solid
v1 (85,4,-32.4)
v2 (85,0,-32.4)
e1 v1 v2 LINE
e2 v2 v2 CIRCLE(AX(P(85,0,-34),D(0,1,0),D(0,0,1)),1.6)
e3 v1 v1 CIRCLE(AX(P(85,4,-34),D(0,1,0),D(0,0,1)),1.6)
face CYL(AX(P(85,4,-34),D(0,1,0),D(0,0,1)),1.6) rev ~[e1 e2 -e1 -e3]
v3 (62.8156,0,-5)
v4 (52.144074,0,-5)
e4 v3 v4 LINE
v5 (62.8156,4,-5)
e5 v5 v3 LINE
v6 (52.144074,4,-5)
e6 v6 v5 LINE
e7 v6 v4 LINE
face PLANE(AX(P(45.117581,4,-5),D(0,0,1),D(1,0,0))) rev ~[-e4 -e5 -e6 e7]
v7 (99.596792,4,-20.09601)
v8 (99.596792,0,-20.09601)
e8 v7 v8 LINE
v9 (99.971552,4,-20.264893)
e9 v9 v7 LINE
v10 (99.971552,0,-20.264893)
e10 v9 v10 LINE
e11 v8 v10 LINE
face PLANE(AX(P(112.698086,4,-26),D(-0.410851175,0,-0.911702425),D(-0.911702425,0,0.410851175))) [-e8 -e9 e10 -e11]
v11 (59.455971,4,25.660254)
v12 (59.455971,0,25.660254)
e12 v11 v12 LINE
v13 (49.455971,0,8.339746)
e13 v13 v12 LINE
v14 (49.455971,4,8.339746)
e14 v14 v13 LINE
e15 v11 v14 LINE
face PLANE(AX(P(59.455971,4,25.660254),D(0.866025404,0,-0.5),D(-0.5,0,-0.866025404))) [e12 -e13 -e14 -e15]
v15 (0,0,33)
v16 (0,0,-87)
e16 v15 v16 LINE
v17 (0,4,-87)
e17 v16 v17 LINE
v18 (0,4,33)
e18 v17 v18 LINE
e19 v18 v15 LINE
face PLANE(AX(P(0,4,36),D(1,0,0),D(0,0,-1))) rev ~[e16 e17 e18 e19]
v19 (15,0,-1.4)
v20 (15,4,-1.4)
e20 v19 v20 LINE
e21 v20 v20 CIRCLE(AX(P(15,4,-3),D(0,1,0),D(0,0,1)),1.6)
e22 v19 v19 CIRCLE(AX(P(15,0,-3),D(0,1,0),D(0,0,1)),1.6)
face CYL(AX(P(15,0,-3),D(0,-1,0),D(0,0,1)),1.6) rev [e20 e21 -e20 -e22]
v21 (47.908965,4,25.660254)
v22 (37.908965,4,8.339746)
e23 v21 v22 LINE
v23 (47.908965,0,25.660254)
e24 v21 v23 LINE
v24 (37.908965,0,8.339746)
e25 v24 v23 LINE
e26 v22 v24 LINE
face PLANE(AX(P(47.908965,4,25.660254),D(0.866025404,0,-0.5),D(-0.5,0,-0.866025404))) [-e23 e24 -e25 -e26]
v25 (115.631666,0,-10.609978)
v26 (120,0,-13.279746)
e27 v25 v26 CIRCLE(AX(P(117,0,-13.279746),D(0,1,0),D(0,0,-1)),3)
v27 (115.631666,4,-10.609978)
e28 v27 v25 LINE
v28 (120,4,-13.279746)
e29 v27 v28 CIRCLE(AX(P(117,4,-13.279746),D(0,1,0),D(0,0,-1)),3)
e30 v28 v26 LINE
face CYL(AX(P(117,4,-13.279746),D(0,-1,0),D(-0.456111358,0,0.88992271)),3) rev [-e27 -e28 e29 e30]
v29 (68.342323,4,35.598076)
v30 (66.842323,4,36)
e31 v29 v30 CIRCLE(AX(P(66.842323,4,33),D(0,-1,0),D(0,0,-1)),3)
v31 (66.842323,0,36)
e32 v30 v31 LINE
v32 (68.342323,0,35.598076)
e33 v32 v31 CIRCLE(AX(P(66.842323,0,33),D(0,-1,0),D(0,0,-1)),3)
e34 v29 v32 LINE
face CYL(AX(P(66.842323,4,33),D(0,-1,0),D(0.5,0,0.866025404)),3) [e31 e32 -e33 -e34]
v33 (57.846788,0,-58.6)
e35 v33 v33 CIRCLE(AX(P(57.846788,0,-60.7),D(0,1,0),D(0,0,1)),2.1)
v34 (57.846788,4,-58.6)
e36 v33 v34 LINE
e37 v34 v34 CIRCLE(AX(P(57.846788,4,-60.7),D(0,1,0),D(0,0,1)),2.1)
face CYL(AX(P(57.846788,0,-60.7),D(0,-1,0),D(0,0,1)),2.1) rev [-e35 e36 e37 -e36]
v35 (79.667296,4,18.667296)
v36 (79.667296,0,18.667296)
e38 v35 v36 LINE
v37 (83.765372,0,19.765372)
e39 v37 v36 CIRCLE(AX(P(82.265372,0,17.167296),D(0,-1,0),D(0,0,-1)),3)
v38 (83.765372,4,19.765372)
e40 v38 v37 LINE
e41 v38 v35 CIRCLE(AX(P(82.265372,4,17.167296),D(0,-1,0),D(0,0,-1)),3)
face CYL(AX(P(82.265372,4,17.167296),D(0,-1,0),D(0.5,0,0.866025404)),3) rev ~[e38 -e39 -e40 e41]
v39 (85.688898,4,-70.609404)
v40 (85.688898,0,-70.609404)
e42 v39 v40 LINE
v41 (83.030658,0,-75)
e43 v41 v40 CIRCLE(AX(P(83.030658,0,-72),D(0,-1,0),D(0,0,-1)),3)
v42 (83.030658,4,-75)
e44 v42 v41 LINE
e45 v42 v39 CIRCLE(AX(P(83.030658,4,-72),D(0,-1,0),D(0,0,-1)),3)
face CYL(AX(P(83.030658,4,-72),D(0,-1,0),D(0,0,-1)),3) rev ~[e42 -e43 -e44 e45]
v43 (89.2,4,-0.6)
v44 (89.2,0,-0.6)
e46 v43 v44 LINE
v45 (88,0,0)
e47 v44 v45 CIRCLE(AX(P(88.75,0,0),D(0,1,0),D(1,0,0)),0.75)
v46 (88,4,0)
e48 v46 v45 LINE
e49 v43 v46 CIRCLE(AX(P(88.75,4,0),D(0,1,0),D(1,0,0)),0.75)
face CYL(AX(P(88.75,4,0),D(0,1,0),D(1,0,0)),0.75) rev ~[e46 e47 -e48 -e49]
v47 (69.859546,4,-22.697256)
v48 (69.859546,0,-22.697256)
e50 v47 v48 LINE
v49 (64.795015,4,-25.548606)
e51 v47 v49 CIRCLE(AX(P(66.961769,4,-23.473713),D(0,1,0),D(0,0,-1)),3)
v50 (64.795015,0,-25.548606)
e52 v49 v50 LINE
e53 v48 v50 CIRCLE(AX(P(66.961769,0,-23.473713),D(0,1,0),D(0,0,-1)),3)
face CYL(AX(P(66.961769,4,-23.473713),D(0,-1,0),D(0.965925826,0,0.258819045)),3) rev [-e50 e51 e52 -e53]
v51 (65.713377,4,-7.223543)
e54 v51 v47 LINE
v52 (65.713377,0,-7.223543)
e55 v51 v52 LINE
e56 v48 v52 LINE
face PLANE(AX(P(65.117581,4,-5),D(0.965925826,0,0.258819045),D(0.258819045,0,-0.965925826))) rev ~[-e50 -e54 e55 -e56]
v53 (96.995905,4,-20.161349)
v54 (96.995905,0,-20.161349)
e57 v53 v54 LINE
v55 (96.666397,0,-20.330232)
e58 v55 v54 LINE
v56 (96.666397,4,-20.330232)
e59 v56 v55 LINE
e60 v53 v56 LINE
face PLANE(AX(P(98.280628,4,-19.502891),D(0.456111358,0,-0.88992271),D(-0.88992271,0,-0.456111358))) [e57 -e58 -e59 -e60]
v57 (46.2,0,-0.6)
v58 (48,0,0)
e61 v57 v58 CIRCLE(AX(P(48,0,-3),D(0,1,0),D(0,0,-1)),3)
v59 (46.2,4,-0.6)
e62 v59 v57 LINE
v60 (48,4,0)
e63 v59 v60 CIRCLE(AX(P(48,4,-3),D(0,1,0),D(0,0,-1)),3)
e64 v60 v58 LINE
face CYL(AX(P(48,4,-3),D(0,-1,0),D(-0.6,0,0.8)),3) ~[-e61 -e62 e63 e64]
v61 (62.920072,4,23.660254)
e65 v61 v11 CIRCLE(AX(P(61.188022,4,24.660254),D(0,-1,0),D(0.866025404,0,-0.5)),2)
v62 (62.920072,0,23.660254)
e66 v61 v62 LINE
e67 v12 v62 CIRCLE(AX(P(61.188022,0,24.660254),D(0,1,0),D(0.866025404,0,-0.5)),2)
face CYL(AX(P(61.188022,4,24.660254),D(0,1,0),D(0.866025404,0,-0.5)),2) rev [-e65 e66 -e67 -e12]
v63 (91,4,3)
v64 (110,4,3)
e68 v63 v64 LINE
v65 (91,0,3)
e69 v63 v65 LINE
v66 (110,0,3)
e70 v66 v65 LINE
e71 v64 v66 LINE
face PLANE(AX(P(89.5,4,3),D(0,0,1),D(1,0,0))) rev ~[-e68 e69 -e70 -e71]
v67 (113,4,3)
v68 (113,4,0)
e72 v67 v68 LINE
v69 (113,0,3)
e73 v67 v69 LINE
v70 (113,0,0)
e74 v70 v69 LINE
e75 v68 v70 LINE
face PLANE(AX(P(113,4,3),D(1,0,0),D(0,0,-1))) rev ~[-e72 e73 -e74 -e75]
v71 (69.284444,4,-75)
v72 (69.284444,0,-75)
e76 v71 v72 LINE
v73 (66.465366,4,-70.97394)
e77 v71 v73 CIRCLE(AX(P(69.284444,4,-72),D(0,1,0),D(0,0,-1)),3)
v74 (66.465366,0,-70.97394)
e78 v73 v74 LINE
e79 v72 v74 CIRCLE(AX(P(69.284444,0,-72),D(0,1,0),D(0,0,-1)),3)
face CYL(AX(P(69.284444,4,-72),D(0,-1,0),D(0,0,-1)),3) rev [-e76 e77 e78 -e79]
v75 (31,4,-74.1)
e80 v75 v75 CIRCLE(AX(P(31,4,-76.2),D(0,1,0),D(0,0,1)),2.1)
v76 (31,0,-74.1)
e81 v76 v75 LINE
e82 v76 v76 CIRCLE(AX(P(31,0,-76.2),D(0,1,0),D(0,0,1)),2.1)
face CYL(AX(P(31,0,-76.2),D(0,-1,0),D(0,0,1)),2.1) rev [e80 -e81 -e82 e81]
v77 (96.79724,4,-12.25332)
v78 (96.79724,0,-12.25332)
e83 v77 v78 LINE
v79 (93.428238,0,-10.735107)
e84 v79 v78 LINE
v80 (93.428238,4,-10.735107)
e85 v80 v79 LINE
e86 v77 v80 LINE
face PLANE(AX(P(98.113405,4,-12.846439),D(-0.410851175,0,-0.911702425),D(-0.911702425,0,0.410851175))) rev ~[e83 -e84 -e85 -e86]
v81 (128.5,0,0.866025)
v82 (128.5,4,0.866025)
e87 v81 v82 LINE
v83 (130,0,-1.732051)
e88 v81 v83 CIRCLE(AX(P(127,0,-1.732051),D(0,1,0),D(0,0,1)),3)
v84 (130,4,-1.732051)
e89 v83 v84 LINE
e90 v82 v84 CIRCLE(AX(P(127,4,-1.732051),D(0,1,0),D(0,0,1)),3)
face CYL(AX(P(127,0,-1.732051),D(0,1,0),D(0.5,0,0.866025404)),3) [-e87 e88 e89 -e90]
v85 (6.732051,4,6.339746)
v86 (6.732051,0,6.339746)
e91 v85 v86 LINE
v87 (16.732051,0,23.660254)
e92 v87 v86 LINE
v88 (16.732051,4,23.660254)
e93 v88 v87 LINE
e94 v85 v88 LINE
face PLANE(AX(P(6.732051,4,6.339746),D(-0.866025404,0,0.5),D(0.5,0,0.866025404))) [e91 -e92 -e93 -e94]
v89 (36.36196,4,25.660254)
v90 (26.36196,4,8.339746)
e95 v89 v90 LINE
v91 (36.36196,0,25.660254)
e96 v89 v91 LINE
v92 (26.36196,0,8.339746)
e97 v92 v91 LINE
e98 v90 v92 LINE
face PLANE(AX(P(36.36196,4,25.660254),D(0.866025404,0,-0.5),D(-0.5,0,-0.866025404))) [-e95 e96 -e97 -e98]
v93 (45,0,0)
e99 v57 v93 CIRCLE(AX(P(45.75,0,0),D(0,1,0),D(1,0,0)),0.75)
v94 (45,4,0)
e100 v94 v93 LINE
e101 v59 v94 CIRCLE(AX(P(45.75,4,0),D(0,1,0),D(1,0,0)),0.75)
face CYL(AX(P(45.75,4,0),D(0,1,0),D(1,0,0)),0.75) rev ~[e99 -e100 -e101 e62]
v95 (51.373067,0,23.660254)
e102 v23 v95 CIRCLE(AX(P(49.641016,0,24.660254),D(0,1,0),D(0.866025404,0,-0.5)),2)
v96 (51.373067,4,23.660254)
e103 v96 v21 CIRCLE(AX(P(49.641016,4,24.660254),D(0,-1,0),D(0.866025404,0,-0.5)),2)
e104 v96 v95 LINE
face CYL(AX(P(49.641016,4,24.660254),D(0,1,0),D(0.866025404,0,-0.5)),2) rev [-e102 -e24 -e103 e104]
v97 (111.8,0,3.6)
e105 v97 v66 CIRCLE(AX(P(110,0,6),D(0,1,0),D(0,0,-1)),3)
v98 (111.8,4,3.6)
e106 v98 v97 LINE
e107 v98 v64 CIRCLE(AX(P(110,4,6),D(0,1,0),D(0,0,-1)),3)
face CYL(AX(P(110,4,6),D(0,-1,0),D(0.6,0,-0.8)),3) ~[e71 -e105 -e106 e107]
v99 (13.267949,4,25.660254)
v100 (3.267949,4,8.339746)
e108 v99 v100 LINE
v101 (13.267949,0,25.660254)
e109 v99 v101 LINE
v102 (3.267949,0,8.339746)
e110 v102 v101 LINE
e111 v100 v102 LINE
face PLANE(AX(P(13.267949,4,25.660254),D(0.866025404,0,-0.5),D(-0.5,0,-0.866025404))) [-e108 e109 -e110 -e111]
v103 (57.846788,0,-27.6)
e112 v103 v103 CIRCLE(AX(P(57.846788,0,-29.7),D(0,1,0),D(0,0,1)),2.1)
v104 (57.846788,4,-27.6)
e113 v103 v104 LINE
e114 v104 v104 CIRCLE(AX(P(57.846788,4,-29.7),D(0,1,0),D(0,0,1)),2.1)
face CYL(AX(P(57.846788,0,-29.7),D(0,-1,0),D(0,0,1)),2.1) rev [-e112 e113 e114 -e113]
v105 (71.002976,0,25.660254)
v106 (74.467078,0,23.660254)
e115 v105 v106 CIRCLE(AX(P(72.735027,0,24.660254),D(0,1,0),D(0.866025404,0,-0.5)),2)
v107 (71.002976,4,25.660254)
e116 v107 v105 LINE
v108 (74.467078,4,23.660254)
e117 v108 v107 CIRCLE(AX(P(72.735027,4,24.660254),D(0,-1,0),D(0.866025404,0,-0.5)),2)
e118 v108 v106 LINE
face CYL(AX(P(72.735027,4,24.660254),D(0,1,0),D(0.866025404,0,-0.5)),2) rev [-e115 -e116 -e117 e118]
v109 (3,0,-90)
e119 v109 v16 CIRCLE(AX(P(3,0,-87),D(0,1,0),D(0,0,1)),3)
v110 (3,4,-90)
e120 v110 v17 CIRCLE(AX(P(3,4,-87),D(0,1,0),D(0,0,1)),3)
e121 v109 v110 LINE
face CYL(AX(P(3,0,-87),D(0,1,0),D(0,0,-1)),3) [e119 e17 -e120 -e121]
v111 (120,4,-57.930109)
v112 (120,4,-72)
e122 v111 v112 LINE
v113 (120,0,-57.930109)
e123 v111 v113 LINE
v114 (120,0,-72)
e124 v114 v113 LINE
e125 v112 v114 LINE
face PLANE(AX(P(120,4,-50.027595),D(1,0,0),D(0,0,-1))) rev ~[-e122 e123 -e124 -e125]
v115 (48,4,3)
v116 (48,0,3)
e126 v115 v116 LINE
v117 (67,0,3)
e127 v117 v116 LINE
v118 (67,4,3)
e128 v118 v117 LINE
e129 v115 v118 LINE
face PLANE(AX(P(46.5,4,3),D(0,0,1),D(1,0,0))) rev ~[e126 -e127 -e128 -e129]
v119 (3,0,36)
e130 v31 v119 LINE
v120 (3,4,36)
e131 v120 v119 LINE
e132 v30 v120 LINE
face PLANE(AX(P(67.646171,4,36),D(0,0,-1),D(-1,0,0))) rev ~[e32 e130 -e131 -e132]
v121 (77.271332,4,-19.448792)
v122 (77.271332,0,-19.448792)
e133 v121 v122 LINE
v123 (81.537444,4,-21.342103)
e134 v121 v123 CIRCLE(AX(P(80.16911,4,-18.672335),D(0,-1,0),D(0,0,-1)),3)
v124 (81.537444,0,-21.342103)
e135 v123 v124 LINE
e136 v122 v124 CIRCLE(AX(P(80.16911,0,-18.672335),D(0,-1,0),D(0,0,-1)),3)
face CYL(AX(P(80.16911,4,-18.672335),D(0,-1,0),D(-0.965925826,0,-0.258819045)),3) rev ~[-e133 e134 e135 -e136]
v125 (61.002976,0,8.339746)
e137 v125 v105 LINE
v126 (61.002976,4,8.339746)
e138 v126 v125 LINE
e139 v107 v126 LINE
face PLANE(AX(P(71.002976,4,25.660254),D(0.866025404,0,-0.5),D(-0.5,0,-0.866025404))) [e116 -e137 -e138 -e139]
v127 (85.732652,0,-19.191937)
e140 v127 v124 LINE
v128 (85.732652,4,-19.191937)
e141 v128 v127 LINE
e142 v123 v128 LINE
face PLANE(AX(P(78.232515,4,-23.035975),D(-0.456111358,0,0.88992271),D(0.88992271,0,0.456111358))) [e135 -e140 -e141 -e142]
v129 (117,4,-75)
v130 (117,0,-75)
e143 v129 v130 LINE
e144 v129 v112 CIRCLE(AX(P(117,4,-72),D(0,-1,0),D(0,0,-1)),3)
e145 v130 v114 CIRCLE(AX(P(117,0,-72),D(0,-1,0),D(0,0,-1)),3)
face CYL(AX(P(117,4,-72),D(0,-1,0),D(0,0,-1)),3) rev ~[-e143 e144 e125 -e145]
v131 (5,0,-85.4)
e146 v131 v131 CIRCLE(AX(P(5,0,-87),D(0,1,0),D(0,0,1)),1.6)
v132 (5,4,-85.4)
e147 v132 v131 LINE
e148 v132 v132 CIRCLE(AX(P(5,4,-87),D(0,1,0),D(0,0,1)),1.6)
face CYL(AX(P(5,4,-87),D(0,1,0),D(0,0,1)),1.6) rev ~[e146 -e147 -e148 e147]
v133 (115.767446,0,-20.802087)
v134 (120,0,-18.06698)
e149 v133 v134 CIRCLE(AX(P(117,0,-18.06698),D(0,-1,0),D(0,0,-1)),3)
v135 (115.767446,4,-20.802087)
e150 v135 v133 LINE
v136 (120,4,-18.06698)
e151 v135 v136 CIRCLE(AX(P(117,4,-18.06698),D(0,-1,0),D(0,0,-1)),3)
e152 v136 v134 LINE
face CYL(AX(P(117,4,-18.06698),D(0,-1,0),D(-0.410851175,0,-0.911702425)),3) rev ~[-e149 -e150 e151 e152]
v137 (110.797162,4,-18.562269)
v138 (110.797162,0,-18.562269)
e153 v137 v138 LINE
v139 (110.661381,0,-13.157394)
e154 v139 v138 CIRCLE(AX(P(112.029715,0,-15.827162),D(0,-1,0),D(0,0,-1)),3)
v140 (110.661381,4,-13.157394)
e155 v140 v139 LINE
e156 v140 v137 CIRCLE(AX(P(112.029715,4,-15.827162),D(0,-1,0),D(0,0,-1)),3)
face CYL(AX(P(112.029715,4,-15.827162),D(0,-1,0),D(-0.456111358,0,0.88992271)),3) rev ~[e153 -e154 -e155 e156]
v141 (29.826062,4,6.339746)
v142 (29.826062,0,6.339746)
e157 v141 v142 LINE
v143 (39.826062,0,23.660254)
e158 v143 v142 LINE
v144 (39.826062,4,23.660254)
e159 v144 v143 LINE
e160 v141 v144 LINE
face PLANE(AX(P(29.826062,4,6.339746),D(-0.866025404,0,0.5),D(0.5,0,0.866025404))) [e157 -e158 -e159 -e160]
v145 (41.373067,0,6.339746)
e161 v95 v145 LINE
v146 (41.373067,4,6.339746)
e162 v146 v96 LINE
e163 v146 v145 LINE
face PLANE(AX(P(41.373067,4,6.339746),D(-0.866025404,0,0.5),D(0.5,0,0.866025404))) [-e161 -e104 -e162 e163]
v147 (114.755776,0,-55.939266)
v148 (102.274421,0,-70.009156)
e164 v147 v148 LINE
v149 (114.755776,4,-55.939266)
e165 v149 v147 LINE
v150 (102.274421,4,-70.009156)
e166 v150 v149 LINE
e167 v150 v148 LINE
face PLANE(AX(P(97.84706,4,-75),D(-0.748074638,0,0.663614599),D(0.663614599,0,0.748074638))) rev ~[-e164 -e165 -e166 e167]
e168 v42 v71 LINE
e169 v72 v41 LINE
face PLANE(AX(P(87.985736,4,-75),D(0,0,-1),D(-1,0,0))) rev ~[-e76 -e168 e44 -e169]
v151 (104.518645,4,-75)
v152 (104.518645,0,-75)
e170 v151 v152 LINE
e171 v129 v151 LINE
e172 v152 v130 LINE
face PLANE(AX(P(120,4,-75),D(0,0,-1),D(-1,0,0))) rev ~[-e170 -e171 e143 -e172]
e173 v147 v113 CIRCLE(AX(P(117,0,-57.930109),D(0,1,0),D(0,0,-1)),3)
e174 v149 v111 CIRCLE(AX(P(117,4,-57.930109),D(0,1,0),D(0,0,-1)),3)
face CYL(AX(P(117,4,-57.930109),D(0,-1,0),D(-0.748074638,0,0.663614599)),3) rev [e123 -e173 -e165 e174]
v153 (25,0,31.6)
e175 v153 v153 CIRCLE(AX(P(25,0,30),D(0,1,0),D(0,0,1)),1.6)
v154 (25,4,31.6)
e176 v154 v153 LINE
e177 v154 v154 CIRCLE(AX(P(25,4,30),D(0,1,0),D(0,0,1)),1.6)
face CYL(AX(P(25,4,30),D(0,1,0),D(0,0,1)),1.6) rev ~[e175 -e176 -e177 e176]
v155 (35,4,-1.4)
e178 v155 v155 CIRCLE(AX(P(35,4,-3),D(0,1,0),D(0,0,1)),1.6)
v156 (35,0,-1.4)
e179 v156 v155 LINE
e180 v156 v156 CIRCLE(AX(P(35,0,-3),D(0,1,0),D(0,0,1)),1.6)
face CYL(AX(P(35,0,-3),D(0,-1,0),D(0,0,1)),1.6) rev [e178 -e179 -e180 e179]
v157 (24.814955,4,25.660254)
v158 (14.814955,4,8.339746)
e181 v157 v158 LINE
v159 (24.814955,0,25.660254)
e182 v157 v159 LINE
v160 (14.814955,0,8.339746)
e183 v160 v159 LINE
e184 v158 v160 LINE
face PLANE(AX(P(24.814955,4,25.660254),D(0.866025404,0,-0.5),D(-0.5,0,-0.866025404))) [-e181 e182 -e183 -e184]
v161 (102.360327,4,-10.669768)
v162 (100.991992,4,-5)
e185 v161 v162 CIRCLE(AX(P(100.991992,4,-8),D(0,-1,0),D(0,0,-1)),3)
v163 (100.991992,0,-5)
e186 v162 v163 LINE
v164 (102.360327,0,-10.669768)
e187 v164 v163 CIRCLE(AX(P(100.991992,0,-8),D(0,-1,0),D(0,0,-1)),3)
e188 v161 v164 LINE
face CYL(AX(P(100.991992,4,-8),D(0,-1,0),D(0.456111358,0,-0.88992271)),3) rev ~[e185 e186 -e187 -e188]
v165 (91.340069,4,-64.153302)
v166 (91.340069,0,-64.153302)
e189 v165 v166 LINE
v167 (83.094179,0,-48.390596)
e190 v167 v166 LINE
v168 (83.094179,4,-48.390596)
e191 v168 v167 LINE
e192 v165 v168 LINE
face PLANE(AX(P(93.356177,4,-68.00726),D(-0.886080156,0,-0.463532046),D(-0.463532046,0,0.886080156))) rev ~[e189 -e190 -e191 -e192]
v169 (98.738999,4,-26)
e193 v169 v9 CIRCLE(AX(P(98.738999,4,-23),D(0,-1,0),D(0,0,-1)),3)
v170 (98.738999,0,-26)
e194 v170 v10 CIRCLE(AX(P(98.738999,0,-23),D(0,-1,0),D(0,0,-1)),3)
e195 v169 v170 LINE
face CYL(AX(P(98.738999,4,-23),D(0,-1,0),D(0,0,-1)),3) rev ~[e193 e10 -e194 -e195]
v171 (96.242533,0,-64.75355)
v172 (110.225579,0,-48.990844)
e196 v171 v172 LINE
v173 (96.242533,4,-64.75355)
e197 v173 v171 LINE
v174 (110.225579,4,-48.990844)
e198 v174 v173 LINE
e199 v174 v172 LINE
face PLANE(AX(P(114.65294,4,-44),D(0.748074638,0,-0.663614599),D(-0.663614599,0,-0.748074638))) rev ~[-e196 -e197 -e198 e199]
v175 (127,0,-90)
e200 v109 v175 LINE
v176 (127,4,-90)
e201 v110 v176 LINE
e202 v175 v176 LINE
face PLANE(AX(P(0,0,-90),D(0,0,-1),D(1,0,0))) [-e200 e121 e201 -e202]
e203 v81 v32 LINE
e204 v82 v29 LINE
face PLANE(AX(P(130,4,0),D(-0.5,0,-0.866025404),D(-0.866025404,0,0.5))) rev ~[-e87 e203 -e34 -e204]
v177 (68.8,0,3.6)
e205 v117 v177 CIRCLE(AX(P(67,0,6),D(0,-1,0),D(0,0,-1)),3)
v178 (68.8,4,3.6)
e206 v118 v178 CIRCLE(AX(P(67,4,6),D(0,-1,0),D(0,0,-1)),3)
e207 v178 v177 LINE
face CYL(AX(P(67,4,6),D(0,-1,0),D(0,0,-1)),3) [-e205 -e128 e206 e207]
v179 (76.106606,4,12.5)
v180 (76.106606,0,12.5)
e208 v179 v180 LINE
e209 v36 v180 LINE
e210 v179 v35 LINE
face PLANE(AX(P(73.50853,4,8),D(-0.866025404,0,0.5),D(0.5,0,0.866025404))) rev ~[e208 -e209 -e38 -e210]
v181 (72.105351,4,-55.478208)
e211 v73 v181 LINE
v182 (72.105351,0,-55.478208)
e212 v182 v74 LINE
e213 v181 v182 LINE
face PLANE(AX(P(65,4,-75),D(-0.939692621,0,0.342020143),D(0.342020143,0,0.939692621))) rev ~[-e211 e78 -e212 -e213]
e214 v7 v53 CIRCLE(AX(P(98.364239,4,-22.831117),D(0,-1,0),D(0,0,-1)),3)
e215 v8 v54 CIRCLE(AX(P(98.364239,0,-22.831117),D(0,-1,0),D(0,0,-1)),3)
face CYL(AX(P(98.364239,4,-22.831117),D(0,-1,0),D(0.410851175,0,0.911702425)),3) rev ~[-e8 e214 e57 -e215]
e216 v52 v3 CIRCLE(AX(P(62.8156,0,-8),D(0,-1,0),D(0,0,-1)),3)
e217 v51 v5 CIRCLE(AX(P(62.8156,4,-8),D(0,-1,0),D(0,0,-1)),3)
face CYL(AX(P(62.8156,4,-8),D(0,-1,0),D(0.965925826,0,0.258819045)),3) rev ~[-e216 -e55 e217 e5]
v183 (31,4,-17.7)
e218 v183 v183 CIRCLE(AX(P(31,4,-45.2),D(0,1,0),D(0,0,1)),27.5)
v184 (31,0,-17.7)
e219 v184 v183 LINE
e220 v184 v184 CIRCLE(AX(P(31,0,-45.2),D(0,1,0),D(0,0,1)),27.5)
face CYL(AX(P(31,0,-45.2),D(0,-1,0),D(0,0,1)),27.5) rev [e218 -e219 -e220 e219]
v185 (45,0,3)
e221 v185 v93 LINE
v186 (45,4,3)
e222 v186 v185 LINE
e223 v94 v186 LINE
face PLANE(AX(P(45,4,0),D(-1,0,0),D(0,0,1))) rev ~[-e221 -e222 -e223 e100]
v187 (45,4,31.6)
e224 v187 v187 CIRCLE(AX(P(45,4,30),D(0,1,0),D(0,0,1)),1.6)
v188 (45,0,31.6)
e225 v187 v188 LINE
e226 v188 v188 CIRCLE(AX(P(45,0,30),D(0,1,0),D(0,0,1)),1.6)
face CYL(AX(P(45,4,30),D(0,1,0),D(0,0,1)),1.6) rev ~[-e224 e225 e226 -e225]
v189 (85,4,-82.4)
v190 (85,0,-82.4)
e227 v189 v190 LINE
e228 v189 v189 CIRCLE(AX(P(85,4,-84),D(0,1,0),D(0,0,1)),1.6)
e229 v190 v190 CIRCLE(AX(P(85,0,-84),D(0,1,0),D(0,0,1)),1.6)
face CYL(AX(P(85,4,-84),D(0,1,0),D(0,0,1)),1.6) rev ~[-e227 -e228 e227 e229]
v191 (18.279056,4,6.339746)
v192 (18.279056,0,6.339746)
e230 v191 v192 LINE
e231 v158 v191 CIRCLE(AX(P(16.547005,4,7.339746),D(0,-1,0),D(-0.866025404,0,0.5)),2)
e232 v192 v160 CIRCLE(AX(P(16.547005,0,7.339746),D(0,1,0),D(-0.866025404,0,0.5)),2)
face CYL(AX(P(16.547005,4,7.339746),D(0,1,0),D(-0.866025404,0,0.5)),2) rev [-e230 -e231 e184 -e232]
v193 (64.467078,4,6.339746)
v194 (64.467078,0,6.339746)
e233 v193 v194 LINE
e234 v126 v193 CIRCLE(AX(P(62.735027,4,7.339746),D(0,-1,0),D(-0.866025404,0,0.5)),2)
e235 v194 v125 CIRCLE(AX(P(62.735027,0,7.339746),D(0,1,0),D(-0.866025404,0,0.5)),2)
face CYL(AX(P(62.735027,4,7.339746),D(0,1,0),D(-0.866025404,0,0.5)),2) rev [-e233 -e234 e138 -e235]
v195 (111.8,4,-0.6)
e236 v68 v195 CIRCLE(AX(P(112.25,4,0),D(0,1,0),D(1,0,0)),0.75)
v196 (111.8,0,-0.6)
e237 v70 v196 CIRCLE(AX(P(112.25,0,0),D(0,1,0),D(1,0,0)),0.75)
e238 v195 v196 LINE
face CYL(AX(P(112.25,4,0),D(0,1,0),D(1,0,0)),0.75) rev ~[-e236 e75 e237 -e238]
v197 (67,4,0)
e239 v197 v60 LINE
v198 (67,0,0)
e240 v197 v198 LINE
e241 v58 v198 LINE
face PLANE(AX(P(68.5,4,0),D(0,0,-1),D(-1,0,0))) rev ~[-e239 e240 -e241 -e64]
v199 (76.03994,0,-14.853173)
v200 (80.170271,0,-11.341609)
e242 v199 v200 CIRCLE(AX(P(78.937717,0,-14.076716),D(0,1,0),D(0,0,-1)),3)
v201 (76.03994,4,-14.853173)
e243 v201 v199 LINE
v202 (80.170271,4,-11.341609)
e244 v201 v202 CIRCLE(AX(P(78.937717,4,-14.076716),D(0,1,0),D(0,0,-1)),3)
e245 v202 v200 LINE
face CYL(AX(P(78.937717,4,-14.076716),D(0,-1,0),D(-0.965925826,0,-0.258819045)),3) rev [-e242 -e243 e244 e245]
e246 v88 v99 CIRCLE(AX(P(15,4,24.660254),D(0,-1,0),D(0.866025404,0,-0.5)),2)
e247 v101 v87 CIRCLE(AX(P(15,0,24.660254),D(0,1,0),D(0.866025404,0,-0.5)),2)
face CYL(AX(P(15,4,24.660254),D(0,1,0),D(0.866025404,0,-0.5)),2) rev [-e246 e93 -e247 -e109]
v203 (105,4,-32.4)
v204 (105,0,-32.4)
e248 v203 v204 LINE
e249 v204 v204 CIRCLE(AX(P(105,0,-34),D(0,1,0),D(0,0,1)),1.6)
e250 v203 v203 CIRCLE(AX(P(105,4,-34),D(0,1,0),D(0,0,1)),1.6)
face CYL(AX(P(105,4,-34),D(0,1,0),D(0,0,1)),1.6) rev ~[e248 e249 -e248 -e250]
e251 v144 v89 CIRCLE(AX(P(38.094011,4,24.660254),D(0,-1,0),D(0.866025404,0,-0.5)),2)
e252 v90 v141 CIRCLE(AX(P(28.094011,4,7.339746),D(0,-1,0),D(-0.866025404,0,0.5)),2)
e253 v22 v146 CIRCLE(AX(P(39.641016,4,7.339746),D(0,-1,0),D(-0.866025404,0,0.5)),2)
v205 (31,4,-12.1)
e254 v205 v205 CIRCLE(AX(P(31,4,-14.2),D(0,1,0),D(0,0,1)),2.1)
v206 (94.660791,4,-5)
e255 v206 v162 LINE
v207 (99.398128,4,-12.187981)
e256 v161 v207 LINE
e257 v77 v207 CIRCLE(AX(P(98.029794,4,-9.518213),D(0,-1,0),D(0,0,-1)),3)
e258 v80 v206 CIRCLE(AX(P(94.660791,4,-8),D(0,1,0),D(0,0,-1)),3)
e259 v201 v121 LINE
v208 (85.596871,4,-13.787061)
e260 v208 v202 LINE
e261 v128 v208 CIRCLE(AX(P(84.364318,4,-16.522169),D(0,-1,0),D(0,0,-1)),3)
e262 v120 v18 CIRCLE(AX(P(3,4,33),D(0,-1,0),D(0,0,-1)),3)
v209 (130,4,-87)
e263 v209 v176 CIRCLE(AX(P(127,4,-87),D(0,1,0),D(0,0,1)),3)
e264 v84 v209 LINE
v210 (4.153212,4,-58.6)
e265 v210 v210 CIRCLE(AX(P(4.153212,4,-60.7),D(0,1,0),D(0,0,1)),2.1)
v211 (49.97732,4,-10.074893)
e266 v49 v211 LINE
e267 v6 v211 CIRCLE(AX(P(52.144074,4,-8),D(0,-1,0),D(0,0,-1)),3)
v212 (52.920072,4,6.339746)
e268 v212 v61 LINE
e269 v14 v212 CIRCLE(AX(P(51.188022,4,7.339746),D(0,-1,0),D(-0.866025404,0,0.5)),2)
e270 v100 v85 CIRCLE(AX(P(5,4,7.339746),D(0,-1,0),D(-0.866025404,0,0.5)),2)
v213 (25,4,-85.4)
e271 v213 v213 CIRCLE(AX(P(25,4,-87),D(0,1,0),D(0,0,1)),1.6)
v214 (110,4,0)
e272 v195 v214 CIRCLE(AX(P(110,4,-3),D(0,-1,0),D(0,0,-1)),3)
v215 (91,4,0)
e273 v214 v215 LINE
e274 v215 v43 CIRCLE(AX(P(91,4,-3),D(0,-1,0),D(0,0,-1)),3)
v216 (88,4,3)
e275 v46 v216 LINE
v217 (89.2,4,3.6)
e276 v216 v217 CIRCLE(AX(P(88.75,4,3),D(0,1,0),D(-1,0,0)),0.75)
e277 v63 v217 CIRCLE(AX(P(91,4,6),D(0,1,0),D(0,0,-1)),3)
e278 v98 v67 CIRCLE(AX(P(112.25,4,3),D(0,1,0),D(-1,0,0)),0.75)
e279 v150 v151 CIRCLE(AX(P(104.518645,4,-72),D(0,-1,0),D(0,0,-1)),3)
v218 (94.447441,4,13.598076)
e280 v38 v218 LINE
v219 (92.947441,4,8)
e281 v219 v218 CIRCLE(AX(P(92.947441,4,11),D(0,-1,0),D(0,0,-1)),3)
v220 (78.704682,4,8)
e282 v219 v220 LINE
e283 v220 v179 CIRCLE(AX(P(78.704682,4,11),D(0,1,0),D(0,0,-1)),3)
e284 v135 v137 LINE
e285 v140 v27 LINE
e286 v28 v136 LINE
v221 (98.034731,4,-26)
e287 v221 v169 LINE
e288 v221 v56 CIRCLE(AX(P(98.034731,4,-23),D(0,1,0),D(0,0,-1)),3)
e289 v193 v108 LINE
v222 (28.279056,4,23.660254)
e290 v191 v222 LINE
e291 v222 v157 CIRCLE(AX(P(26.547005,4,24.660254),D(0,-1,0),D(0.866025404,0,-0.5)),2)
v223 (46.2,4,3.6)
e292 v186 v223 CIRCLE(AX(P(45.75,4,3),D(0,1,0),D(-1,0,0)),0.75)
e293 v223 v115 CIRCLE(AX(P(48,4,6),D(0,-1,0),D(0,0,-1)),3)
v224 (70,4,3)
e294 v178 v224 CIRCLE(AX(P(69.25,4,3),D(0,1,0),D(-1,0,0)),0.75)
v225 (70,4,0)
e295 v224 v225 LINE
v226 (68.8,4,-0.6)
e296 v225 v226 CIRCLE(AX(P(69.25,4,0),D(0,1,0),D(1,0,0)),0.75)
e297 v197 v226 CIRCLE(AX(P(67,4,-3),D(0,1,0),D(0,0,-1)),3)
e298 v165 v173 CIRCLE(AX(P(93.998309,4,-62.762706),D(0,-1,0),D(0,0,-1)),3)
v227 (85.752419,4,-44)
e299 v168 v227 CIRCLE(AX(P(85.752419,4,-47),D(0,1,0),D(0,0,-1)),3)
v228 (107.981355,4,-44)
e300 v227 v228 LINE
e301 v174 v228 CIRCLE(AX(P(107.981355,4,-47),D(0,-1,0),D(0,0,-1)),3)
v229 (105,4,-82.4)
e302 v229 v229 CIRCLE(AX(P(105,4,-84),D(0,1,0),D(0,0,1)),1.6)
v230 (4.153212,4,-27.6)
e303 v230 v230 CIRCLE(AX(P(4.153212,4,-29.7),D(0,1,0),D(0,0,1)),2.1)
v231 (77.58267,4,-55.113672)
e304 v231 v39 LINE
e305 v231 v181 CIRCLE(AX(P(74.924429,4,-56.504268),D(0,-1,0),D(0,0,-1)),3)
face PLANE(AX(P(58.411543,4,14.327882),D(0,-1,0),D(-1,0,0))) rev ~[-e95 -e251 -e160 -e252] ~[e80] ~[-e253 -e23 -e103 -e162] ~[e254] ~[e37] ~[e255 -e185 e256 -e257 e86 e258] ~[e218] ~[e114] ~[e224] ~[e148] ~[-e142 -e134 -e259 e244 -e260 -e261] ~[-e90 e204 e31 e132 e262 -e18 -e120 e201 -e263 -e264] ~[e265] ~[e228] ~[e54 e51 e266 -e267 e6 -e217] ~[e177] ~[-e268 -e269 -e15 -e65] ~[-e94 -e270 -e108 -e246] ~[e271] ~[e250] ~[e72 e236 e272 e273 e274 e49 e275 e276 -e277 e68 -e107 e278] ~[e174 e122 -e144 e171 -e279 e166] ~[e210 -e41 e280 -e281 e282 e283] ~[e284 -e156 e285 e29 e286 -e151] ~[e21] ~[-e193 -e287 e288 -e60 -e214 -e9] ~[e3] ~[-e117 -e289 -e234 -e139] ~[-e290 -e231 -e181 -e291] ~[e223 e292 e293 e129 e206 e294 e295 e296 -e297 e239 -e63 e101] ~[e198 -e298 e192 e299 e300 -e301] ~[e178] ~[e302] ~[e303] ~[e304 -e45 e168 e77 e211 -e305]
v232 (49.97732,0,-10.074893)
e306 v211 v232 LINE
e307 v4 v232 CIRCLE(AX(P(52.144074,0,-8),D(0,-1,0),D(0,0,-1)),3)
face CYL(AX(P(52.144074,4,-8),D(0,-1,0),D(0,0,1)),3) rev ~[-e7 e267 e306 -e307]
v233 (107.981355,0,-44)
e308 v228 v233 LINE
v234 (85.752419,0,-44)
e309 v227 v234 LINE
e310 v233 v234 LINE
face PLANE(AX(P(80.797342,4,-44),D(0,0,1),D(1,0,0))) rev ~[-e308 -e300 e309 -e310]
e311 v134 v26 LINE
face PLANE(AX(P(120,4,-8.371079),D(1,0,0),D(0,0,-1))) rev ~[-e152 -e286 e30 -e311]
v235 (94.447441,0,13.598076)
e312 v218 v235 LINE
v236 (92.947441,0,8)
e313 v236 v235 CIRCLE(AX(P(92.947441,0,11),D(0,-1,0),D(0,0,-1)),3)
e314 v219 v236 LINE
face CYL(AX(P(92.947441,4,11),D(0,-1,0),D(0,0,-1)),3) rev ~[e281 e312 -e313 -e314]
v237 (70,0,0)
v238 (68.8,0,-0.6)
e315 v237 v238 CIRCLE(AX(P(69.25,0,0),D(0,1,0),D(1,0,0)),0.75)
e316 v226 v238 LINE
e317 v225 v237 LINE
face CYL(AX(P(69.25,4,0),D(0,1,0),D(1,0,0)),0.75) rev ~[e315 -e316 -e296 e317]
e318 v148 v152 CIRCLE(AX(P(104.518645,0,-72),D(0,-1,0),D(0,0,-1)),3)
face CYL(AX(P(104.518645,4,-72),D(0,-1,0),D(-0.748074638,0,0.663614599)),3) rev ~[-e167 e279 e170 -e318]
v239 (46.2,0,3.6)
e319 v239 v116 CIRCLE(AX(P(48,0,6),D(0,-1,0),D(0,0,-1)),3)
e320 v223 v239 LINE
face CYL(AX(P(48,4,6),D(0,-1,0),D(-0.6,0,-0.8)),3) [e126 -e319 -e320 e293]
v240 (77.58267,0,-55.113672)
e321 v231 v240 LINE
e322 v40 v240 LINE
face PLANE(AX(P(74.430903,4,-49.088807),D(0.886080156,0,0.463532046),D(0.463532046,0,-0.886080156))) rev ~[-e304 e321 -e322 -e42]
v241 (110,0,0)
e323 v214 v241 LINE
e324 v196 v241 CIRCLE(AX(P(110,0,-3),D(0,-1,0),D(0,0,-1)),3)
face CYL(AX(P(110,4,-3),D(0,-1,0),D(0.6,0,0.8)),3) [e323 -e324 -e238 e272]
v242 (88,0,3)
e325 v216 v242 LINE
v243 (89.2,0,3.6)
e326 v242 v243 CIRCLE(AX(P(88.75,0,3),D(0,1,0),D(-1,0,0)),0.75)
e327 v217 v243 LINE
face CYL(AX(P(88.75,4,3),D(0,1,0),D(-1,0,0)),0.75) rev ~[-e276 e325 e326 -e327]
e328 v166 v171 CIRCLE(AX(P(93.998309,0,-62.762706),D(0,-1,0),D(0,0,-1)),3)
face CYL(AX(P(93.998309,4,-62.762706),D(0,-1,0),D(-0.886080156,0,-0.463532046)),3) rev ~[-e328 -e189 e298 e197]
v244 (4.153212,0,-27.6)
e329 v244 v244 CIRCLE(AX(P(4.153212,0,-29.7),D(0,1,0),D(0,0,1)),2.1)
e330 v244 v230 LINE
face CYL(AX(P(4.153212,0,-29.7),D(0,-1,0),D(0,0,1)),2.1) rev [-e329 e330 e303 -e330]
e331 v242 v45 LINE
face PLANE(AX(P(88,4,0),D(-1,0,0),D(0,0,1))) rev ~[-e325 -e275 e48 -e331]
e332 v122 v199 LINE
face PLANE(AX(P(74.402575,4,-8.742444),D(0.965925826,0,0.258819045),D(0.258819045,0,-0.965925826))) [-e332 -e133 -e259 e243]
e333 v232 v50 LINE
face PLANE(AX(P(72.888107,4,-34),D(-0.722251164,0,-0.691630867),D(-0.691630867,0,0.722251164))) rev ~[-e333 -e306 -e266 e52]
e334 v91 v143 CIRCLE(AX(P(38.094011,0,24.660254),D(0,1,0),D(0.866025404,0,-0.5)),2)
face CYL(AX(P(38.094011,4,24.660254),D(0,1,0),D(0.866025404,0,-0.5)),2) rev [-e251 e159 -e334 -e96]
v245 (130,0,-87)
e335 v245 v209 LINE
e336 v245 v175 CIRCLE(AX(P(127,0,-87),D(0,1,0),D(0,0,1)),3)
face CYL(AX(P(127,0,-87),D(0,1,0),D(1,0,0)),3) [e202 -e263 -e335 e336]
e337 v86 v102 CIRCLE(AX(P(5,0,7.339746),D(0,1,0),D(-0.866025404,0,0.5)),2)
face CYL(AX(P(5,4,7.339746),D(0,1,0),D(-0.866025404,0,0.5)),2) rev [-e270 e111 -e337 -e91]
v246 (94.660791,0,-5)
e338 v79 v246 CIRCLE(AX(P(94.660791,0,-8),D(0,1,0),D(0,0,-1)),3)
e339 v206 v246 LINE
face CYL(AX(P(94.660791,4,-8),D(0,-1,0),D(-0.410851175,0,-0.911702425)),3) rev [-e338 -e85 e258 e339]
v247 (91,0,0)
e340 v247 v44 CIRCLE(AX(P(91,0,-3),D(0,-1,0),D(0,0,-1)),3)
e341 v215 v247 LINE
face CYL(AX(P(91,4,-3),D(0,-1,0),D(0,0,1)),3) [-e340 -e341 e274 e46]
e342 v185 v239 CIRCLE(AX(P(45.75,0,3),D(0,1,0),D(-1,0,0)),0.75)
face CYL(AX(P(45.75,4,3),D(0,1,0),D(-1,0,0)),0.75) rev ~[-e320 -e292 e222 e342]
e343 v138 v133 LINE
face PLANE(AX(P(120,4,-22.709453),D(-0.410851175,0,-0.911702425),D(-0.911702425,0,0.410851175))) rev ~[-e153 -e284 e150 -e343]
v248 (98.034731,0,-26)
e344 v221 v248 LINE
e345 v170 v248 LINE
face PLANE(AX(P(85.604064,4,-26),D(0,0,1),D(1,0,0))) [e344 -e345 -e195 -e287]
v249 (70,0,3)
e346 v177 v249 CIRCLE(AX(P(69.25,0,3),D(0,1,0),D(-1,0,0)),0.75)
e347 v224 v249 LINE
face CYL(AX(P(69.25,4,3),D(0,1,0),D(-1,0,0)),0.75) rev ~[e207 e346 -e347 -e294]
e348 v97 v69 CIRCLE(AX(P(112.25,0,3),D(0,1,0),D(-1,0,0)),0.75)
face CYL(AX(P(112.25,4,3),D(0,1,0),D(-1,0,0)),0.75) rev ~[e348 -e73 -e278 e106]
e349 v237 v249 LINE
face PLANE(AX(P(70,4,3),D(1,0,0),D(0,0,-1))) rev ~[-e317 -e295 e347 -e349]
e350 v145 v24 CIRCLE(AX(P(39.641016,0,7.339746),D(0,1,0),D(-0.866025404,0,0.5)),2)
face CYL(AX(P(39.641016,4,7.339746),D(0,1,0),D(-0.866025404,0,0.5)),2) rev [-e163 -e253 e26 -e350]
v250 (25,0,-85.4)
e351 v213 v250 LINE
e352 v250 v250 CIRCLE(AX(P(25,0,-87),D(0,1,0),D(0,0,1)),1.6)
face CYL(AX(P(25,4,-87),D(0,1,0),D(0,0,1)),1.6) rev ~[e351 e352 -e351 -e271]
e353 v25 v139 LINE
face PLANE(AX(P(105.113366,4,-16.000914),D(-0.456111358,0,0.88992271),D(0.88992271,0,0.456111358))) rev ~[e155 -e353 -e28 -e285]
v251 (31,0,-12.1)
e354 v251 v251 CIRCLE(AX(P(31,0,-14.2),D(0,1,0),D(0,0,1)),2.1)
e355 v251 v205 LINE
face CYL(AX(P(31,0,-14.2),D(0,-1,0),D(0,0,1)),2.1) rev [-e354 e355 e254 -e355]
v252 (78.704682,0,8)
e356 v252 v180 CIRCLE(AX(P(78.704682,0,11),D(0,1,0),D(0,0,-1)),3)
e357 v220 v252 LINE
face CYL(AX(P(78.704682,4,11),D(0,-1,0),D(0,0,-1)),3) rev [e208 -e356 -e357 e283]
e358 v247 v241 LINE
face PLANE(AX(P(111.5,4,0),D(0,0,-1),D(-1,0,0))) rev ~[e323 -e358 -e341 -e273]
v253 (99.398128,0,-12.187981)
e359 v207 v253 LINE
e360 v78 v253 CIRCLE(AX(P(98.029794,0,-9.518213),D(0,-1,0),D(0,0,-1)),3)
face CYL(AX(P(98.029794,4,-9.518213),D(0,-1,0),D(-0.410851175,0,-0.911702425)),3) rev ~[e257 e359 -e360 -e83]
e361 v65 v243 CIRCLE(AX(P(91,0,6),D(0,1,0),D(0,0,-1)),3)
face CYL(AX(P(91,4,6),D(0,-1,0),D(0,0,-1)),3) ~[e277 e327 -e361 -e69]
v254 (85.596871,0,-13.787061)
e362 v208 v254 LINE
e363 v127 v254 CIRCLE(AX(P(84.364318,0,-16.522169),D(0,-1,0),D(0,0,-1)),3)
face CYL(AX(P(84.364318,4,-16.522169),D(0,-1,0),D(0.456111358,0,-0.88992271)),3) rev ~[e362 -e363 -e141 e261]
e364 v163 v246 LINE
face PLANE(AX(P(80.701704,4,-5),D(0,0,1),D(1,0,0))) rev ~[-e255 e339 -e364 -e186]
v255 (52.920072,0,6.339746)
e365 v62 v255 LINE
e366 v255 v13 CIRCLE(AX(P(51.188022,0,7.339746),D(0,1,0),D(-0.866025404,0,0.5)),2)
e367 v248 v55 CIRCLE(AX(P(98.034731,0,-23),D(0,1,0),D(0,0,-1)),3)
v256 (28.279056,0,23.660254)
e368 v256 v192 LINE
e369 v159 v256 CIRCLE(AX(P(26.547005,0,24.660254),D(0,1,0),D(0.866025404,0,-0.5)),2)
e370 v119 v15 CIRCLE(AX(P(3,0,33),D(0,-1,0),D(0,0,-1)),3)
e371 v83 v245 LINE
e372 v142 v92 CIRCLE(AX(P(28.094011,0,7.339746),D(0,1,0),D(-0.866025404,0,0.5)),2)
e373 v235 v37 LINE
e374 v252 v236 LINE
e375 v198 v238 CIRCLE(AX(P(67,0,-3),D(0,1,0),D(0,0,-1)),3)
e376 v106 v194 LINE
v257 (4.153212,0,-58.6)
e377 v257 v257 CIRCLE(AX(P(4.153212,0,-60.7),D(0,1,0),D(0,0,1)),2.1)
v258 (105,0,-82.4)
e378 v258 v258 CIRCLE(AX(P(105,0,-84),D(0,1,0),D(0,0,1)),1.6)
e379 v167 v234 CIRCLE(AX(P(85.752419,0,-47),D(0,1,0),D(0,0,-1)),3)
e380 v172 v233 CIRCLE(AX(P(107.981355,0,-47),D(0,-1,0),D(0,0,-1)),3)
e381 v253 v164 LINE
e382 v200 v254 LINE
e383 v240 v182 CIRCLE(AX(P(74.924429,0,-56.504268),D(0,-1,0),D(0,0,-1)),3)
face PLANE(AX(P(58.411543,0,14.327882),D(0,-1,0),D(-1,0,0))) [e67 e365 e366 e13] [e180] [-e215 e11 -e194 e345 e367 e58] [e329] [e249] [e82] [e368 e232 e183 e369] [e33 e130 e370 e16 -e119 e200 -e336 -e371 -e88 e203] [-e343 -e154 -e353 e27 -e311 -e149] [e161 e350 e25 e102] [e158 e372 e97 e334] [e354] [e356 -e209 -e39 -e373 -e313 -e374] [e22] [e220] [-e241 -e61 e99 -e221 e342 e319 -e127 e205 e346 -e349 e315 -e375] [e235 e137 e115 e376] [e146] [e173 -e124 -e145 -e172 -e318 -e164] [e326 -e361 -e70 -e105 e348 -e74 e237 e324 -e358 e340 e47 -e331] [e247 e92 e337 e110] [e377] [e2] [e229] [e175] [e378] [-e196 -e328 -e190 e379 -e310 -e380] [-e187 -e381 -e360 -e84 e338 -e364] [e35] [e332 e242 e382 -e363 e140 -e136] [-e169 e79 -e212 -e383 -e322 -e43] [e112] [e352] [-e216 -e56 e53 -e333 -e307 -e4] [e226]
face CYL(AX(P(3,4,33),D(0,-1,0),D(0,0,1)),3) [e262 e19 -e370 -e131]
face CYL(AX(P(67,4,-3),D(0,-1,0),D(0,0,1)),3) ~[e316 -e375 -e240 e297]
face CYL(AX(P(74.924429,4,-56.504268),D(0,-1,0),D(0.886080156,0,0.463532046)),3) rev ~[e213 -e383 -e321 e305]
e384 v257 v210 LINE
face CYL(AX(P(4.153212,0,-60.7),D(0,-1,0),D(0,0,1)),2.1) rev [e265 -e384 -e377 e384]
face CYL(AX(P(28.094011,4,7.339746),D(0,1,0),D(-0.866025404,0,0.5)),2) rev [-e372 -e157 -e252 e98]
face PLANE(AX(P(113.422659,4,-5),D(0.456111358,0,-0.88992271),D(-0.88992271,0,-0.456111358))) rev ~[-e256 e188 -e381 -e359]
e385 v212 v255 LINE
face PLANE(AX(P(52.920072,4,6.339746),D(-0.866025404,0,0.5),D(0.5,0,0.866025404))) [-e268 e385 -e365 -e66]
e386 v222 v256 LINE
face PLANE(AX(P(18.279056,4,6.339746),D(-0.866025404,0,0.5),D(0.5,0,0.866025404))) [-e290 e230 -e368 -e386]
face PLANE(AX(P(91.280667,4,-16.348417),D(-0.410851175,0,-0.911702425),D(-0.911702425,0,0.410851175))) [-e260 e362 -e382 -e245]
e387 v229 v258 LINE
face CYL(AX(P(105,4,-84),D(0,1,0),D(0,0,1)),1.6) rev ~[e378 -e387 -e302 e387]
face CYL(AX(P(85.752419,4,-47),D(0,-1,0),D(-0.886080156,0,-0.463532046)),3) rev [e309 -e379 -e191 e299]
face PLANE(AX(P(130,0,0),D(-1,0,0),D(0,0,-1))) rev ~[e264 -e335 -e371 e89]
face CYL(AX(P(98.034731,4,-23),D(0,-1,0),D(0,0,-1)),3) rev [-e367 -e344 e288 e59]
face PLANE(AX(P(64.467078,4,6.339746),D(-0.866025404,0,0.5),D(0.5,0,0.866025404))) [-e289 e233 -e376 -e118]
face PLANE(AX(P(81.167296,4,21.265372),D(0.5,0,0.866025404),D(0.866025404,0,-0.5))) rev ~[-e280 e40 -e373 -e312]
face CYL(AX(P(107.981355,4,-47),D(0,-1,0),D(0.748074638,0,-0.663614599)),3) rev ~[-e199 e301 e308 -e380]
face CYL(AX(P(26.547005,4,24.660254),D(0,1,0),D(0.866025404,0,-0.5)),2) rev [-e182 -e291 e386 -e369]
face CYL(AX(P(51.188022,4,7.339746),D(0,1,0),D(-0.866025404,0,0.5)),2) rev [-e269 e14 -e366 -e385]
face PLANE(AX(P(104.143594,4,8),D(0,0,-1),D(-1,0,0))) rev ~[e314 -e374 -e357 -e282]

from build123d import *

# Parameters (mm, degrees)
SKETCH_1_W          = 130
SKETCH_1_H          = 90
SKETCH_1_R          = 27.5
SKETCH_1_R_2        = 2.1
SKETCH_1_R_3        = 1.6
EXTRUDE_1_DEPTH     = 4
EXTRUDE_2_DEPTH     = 4
SKETCH_3_R          = 1.6
CUT_EXTRUDE_1_DEPTH = 10
SKETCH_4_R          = 1.6
CUT_EXTRUDE_2_DEPTH = 10
CUT_EXTRUDE_3_DEPTH = 10
FILLET_1_R          = 3
CUT_EXTRUDE_4_DEPTH = 10
FILLET_2_R          = 3


with BuildPart() as part:
    # 草图1 → 凸台-拉伸1 (new body)
    with BuildSketch(Plane(origin=(0, 0, 0), x_dir=(1, 0, 0), z_dir=(0, 1, 0))):
        with Locations((65, 45)):
            Rectangle(SKETCH_1_W, SKETCH_1_H)
        with Locations(Location((31, 45.2, 0), (0, 0, 270))):
            Circle(SKETCH_1_R, mode=Mode.SUBTRACT)
        with Locations(Location((31, 76.2, 0), (0, 0, 270))):
            Circle(SKETCH_1_R_2, mode=Mode.SUBTRACT)
        with Locations(Location((57.846787517, 60.7, 0), (0, 0, 270))):
            Circle(SKETCH_1_R_2, mode=Mode.SUBTRACT)
        with Locations(Location((57.846787517, 29.7, 0), (0, 0, 270))):
            Circle(SKETCH_1_R_2, mode=Mode.SUBTRACT)
        with Locations(Location((31, 14.2, 0), (0, 0, 270))):
            Circle(SKETCH_1_R_2, mode=Mode.SUBTRACT)
        with Locations(Location((4.153212483, 29.7, 0), (0, 0, 270))):
            Circle(SKETCH_1_R_2, mode=Mode.SUBTRACT)
        with Locations(Location((4.153212483, 60.7, 0), (0, 0, 270))):
            Circle(SKETCH_1_R_2, mode=Mode.SUBTRACT)
        with Locations(Location((15, 3, 0), (0, 0, 270))):
            Circle(SKETCH_1_R_3, mode=Mode.SUBTRACT)
        with Locations(Location((35, 3, 0), (0, 0, 270))):
            Circle(SKETCH_1_R_3, mode=Mode.SUBTRACT)
    extrude(amount=EXTRUDE_1_DEPTH)

    # 草图2 → 凸台-拉伸2 (add)
    with BuildSketch(Plane(origin=(0, 4, 0), x_dir=(1, 0, 0), z_dir=(0, 1, 0))):
        Polygon((130, 0), (67.646170928, -36), (0, -36), (0, 0), align=None)
    extrude(amount=-EXTRUDE_2_DEPTH)

    # 草图3 → 切除-拉伸1 (cut)
    with BuildSketch(Plane(origin=(0, 4, 0), x_dir=(1, 0, 0), z_dir=(0, 1, 0))):
        with Locations(Location((25, -30, 0), (0, 0, 270))):
            Circle(SKETCH_3_R)
        with Locations(Location((45, -30, 0), (0, 0, 270))):
            Circle(SKETCH_3_R)
    extrude(amount=-CUT_EXTRUDE_1_DEPTH, mode=Mode.SUBTRACT)

    # 草图4 → 切除-拉伸2 (cut)
    with BuildSketch(Plane(origin=(0, 4, 0), x_dir=(1, 0, 0), z_dir=(0, 1, 0))):
        with Locations(Location((85, 84, 0), (0, 0, 270))):
            Circle(SKETCH_4_R)
        with Locations(Location((105, 84, 0), (0, 0, 270))):
            Circle(SKETCH_4_R)
        with Locations(Location((85, 34, 0), (0, 0, 270))):
            Circle(SKETCH_4_R)
        with Locations(Location((105, 34, 0), (0, 0, 270))):
            Circle(SKETCH_4_R)
        with Locations(Location((5, 87, 0), (0, 0, 270))):
            Circle(SKETCH_4_R)
        with Locations(Location((25, 87, 0), (0, 0, 270))):
            Circle(SKETCH_4_R)
    extrude(amount=-CUT_EXTRUDE_2_DEPTH, mode=Mode.SUBTRACT)

    # 草图2<3> → 切除-拉伸3 (cut)
    with BuildSketch(Plane(origin=(0, 4, 0), x_dir=(1, 0, 0), z_dir=(0, 1, 0))):
        with BuildLine():
            Line((46.5, 0), (45, 0))
            Line((45, 0), (45, -3))
            ThreePointArc((45, -3), (45.75, -3.75), (46.5, -3))
            Line((46.5, -3), (68.5, -3))
            ThreePointArc((68.5, -3), (69.25, -3.75), (70, -3))
            Line((70, -3), (70, 0))
            Line((70, 0), (68.5, 0))
            Line((68.5, 0), (46.5, 0))
        make_face()
        with BuildLine():
            Line((113, -3), (113, 0))
            Line((113, 0), (111.5, 0))
            Line((111.5, 0), (89.5, 0))
            Line((89.5, 0), (88, 0))
            Line((88, 0), (88, -3))
            ThreePointArc((88, -3), (88.75, -3.75), (89.5, -3))
            Line((89.5, -3), (111.5, -3))
            ThreePointArc((111.5, -3), (112.25, -3.75), (113, -3))
        make_face()
        with BuildLine():
            ThreePointArc((46.5, 0), (45.75, 0.75), (45, 0))
            Line((45, 0), (46.5, 0))
        make_face()
        with BuildLine():
            Line((68.5, 0), (70, 0))
            ThreePointArc((70, 0), (69.25, 0.75), (68.5, 0))
        make_face()
        with BuildLine():
            Line((88, 0), (89.5, 0))
            ThreePointArc((89.5, 0), (88.75, 0.75), (88, 0))
        make_face()
        with BuildLine():
            Line((111.5, 0), (113, 0))
            ThreePointArc((113, 0), (112.25, 0.75), (111.5, 0))
        make_face()
    extrude(amount=-CUT_EXTRUDE_3_DEPTH, mode=Mode.SUBTRACT)

    # 圆角1
    fillet_1_edges = [part.edges().sort_by_distance(p)[0] for p in [
        (67.646170928, 2, 36),
        (0, 2, 36),
        (0, 2, -90),
        (130, 2, -90),
        (130, 2, 0),
    ]]
    fillet(fillet_1_edges, radius=FILLET_1_R)

    # 草图5 → 切除-拉伸4 (cut)
    with BuildSketch(Plane(origin=(0, 4, 0), x_dir=(1, 0, 0), z_dir=(0, 1, 0))):
        with BuildLine():
            Line((6.732050808, -6.339745962), (16.732050808, -23.660254038))
            ThreePointArc((16.732050808, -23.660254038), (16, -26.392304845), (13.267949192, -25.660254038))
            Line((13.267949192, -25.660254038), (3.267949192, -8.339745962))
            ThreePointArc((3.267949192, -8.339745962), (4, -5.607695155), (6.732050808, -6.339745962))
        make_face()
        with BuildLine():
            Line((18.279056191, -6.339745962), (28.279056191, -23.660254038))
            ThreePointArc((28.279056191, -23.660254038), (27.547005384, -26.392304845), (24.814954576, -25.660254038))
            Line((24.814954576, -25.660254038), (14.814954576, -8.339745962))
            ThreePointArc((14.814954576, -8.339745962), (15.547005384, -5.607695155), (18.279056191, -6.339745962))
        make_face()
        with BuildLine():
            Line((29.826061575, -6.339745962), (39.826061575, -23.660254038))
            ThreePointArc((39.826061575, -23.660254038), (39.094010768, -26.392304845), (36.36195996, -25.660254038))
            Line((36.36195996, -25.660254038), (26.36195996, -8.339745962))
            ThreePointArc((26.36195996, -8.339745962), (27.094010768, -5.607695155), (29.826061575, -6.339745962))
        make_face()
        with BuildLine():
            Line((41.373066959, -6.339745962), (51.373066959, -23.660254038))
            ThreePointArc((51.373066959, -23.660254038), (50.641016151, -26.392304845), (47.908965344, -25.660254038))
            Line((47.908965344, -25.660254038), (37.908965344, -8.339745962))
            ThreePointArc((37.908965344, -8.339745962), (38.641016151, -5.607695155), (41.373066959, -6.339745962))
        make_face()
        with BuildLine():
            Line((52.920072343, -6.339745962), (62.920072343, -23.660254038))
            ThreePointArc((62.920072343, -23.660254038), (62.188021535, -26.392304845), (59.455970728, -25.660254038))
            Line((59.455970728, -25.660254038), (49.455970728, -8.339745962))
            ThreePointArc((49.455970728, -8.339745962), (50.188021535, -5.607695155), (52.920072343, -6.339745962))
        make_face()
        with BuildLine():
            Line((64.467077727, -6.339745962), (74.467077727, -23.660254038))
            ThreePointArc((74.467077727, -23.660254038), (73.735026919, -26.392304845), (71.002976111, -25.660254038))
            Line((71.002976111, -25.660254038), (61.002976111, -8.339745962))
            ThreePointArc((61.002976111, -8.339745962), (61.735026919, -5.607695155), (64.467077727, -6.339745962))
        make_face()
        Polygon((73.508529611, -8), (81.167295593, -21.265371804), (104.143593539, -8), align=None)
        Polygon((65, 75), (74.430902982, 49.088807011), (87.985735716, 75), align=None)
        Polygon((80.797341547, 44), (114.652939968, 44), (93.356176649, 68.007260469), align=None)
        Polygon((120, 50.027594945), (120, 75), (97.847060032, 75), align=None)
        Polygon((72.888107353, 34), (45.117580773, 5), (65.117580773, 5), align=None)
        Polygon((80.701704351, 5), (113.42265886, 5), (98.11340514, 12.846439281), align=None)
        Polygon((74.402575084, 8.742444076), (78.232515284, 23.035975491), (91.280667048, 16.348416944), align=None)
        Polygon((85.604064397, 26), (112.698085865, 26), (98.280627632, 19.502891419), align=None)
        Polygon((120, 8.371079272), (120, 22.709452649), (105.113365724, 16.000913756), align=None)
    extrude(amount=-CUT_EXTRUDE_4_DEPTH, mode=Mode.SUBTRACT)

    # 圆角2
    fillet_2_edges = [part.edges().sort_by_distance(p)[0] for p in [
        (68.5, 2, 3),
        (46.5, 2, 3),
        (46.5, 2, 0),
        (68.5, 2, 0),
        (111.5, 2, 3),
        (89.5, 2, 3),
        (89.5, 2, 0),
        (111.5, 2, 0),
        (65, 2, -75),
        (87.985735716, 2, -75),
        (74.430902982, 2, -49.088807011),
        (97.847060032, 2, -75),
        (120, 2, -75),
        (120, 2, -50.027594945),
        (73.508529611, 2, 8),
        (104.143593539, 2, 8),
        (81.167295593, 2, 21.265371804),
        (112.698085865, 2, -26),
        (98.280627632, 2, -19.502891419),
        (85.604064397, 2, -26),
        (78.232515284, 2, -23.035975491),
        (91.280667048, 2, -16.348416944),
        (74.402575084, 2, -8.742444076),
        (80.797341547, 2, -44),
        (93.356176649, 2, -68.007260469),
        (114.652939968, 2, -44),
        (72.888107353, 2, -34),
        (65.117580773, 2, -5),
        (45.117580773, 2, -5),
        (120, 2, -8.371079272),
        (105.113365724, 2, -16.000913756),
        (120, 2, -22.709452649),
        (98.11340514, 2, -12.846439281),
        (113.42265886, 2, -5),
        (80.701704351, 2, -5),
    ]]
    fillet(fillet_2_edges, radius=FILLET_2_R)


solid = part.part
